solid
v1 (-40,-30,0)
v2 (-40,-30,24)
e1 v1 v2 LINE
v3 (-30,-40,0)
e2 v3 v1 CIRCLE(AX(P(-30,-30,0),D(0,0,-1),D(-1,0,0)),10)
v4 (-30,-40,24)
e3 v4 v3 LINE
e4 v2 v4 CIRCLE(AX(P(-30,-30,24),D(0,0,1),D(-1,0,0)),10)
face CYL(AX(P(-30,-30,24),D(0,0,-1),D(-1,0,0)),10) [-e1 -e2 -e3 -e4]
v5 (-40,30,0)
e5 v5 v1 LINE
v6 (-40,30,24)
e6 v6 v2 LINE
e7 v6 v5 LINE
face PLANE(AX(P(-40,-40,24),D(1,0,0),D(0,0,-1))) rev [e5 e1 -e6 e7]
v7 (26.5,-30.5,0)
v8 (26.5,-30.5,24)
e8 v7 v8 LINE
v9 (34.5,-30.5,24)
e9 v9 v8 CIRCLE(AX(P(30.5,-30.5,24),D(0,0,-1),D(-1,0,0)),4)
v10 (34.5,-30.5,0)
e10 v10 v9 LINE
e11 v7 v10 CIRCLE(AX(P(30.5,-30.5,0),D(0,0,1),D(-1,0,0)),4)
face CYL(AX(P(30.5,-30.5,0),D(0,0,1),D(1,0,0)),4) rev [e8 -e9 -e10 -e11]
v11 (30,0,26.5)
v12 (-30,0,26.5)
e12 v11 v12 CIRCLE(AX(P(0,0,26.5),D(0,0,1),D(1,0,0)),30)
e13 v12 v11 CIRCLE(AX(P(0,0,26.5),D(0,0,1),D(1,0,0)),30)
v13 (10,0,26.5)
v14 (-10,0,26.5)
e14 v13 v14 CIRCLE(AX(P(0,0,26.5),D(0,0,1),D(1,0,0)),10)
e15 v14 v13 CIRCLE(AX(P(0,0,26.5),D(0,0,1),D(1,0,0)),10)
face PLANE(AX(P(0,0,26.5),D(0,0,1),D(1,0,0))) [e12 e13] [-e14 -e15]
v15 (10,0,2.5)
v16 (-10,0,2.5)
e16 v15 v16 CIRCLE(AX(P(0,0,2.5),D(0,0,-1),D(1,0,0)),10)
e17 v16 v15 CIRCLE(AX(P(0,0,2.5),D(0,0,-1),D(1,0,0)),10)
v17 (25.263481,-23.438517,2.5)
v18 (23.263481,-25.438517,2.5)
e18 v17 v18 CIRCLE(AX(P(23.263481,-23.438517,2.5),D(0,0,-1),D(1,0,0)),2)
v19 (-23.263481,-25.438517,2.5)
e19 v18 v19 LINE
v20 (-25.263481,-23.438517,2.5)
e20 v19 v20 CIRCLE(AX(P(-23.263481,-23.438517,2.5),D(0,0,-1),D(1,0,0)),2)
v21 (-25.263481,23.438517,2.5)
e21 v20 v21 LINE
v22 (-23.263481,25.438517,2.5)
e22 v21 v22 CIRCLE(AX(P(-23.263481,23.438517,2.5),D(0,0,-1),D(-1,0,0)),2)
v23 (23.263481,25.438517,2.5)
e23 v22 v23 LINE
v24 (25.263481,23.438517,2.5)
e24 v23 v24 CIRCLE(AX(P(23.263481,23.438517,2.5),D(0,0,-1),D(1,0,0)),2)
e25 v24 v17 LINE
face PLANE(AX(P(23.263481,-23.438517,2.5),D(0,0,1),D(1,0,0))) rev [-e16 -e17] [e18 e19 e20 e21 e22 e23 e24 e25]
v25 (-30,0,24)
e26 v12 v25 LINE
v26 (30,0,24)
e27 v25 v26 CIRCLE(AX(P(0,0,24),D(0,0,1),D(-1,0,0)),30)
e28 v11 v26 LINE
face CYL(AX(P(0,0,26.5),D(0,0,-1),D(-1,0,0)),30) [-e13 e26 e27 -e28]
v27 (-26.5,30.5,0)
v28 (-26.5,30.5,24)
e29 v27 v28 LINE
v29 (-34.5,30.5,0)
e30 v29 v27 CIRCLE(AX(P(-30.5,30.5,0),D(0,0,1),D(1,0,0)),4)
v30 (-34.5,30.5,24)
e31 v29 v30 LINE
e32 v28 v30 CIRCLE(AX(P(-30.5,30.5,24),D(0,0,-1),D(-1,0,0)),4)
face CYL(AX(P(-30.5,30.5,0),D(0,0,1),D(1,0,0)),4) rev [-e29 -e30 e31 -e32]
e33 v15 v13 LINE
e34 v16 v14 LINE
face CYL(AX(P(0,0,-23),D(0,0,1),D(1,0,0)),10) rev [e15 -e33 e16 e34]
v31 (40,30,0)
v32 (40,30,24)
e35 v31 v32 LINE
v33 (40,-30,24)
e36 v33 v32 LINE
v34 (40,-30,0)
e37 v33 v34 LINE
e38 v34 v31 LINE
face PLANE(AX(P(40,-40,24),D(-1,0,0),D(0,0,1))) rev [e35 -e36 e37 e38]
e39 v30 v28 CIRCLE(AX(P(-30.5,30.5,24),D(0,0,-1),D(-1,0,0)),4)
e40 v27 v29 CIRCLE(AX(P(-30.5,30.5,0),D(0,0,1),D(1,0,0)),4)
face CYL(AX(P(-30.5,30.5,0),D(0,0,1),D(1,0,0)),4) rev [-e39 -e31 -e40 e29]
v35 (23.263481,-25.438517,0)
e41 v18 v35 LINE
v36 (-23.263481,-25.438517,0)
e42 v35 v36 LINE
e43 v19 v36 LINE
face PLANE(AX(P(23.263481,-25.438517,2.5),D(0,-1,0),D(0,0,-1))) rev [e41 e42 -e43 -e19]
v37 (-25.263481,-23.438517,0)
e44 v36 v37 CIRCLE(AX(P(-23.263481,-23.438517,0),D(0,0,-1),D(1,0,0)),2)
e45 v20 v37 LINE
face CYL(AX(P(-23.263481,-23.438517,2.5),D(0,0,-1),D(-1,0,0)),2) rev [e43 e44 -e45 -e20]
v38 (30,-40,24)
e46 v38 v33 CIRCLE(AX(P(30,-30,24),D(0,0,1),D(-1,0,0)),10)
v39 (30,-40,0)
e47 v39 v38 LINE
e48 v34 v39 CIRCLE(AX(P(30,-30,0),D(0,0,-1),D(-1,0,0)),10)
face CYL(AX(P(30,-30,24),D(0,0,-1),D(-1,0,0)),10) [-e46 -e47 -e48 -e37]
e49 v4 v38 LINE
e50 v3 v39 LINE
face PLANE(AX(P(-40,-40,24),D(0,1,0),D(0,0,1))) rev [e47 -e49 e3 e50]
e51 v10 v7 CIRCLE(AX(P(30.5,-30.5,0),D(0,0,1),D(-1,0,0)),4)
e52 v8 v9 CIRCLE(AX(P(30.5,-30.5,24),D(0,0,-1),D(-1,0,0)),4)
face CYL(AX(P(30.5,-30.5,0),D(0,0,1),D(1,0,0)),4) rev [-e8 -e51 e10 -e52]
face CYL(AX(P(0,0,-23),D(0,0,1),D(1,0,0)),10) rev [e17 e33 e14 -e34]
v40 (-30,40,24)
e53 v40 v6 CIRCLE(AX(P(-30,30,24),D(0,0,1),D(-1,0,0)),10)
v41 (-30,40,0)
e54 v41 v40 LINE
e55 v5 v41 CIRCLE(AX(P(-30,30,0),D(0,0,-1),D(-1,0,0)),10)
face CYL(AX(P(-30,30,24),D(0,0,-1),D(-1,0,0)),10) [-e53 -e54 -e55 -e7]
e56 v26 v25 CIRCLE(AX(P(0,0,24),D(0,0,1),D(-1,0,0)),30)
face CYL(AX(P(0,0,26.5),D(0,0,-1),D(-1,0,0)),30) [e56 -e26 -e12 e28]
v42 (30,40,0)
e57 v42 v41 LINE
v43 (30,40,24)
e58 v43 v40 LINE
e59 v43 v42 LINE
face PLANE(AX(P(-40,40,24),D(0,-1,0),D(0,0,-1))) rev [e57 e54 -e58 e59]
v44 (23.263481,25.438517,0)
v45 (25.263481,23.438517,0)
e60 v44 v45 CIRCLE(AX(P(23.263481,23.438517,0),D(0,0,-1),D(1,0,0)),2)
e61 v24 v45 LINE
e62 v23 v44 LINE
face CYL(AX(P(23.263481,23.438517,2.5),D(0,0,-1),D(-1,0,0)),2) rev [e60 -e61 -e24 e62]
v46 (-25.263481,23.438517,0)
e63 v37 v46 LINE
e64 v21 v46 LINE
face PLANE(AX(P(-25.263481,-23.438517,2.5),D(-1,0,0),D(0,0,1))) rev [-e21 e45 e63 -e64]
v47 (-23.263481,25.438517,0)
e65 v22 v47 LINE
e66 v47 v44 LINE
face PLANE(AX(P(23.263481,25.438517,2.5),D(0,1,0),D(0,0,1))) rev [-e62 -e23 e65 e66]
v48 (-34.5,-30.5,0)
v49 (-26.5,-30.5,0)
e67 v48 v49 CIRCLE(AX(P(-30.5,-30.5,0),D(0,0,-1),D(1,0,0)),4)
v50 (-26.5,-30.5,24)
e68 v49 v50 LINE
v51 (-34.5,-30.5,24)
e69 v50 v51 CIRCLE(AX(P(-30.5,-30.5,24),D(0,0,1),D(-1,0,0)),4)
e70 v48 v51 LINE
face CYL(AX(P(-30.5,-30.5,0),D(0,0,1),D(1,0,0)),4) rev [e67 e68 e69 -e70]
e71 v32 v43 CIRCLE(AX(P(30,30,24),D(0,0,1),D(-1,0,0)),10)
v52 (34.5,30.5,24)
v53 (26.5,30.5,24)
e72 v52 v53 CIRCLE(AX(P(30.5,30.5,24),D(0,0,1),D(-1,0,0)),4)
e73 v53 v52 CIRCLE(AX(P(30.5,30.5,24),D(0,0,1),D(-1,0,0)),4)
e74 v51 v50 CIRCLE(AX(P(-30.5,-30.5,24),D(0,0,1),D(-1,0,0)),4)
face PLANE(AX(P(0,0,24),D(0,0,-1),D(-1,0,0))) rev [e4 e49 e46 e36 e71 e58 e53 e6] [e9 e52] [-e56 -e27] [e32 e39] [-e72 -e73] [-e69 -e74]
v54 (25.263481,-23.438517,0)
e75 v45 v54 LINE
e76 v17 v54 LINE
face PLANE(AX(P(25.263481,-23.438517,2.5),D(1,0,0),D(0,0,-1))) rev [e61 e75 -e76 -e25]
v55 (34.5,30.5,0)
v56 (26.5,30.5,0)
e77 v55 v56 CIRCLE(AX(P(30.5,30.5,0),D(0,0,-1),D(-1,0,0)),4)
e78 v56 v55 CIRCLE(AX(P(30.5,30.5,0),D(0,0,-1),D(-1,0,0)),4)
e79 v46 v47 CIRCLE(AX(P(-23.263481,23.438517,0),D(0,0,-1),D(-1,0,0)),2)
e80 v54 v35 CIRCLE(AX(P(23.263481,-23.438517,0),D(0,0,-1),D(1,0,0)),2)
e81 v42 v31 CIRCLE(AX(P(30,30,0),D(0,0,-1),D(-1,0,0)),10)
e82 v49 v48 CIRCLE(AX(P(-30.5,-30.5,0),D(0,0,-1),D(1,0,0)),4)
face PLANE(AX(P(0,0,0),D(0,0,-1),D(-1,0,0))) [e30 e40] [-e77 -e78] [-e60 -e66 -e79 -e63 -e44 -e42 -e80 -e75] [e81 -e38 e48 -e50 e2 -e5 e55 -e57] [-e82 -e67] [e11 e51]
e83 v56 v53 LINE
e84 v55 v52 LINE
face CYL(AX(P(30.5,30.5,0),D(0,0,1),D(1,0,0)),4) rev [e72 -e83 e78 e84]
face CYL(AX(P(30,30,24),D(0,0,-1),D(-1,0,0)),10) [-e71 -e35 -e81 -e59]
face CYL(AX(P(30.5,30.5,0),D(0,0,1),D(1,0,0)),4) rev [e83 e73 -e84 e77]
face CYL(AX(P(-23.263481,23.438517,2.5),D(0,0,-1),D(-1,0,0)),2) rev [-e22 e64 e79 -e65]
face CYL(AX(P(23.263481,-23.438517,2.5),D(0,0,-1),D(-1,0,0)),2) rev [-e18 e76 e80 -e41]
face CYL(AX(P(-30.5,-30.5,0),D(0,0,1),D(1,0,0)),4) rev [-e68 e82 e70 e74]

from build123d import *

# Parameters (mm, degrees)
SKETCH_1_W               = 80
SKETCH_1_H               = 80
EXTRUDE_1_DEPTH          = 24
FILLET_1_R               = 10
SKETCH_2_R               = 4
CUT_EXTRUDE_1_DEPTH      = 62.449165983
MIRROR_2_COPY_1_SKETCH_R = 4
MIRROR_2_COPY_1_DEPTH    = 62.449165983
SKETCH_3_R               = 30
EXTRUDE_2_DEPTH          = 2.5
SKETCH_4_R               = 10
CUT_EXTRUDE_2_DEPTH      = 49.5
CUT_EXTRUDE_3_DEPTH      = 2.5


with BuildPart() as part:
    # 草图1 → 凸台-拉伸1 (new body)
    with BuildSketch(Plane.XY):
        Rectangle(SKETCH_1_W, SKETCH_1_H)
    extrude(amount=EXTRUDE_1_DEPTH)

    # 圆角1
    fillet_1_edges = [part.edges().sort_by_distance(p)[0] for p in [
        (40, -40, 12),
        (-40, -40, 12),
        (-40, 40, 12),
        (40, 40, 12),
    ]]
    fillet(fillet_1_edges, radius=FILLET_1_R)

    # 草图2 → 切除-拉伸1 (cut, symmetric)
    with BuildSketch(Plane.XY.offset(24)):
        with Locations((-30.5, 30.5)):
            Circle(SKETCH_2_R)
    cut_extrude_1 = extrude(amount=CUT_EXTRUDE_1_DEPTH, both=True, mode=Mode.SUBTRACT)

    # 镜向1: 切除-拉伸1 across plane
    add(cut_extrude_1.mirror(Plane.ZX), mode=Mode.SUBTRACT)

    # 镜向2: 切除-拉伸1 across plane
    add(cut_extrude_1.mirror(Plane(origin=(0, 0, 0), x_dir=(0, 0, 1), z_dir=(1, 0, 0))), mode=Mode.SUBTRACT)

    # 镜向2 copy 1 sketch → 镜向2 copy 1 (cut, symmetric)
    with BuildSketch(Plane(origin=(0, 0, 24), x_dir=(-1, 0, 0), z_dir=(0, 0, 1))):
        with Locations((-30.5, 30.5)):
            Circle(MIRROR_2_COPY_1_SKETCH_R)
    extrude(amount=MIRROR_2_COPY_1_DEPTH, both=True, mode=Mode.SUBTRACT)

    # 草图3 → 凸台-拉伸2 (add)
    with BuildSketch(Plane.XY.offset(24)):
        with Locations(Location((0, 0, 0), (0, 0, 180))):
            Circle(SKETCH_3_R)
    extrude(amount=EXTRUDE_2_DEPTH)

    # 草图4 → 切除-拉伸2 (cut)
    with BuildSketch(Plane.XY.offset(26.5)):
        Circle(SKETCH_4_R)
    extrude(amount=-CUT_EXTRUDE_2_DEPTH, mode=Mode.SUBTRACT)

    # 草图5 → 切除-拉伸3 (cut)
    with BuildSketch(Plane(origin=(0, 0, 0), x_dir=(-1, 0, 0), z_dir=(0, 0, -1))):
        with BuildLine():
            Line((-23.263481458, -25.438517127), (23.263481458, -25.438517127))
            ThreePointArc((23.263481458, -25.438517127), (24.677695021, -24.852730689), (25.263481458, -23.438517127))
            Line((25.263481458, -23.438517127), (25.263481458, 23.438517127))
            ThreePointArc((25.263481458, 23.438517127), (24.677695021, 24.852730689), (23.263481458, 25.438517127))
            Line((23.263481458, 25.438517127), (-23.263481458, 25.438517127))
            ThreePointArc((-23.263481458, 25.438517127), (-24.677695021, 24.852730689), (-25.263481458, 23.438517127))
            Line((-25.263481458, 23.438517127), (-25.263481458, -23.438517127))
            ThreePointArc((-25.263481458, -23.438517127), (-24.677695021, -24.852730689), (-23.263481458, -25.438517127))
        make_face()
    extrude(amount=-CUT_EXTRUDE_3_DEPTH, mode=Mode.SUBTRACT)


solid = part.part
